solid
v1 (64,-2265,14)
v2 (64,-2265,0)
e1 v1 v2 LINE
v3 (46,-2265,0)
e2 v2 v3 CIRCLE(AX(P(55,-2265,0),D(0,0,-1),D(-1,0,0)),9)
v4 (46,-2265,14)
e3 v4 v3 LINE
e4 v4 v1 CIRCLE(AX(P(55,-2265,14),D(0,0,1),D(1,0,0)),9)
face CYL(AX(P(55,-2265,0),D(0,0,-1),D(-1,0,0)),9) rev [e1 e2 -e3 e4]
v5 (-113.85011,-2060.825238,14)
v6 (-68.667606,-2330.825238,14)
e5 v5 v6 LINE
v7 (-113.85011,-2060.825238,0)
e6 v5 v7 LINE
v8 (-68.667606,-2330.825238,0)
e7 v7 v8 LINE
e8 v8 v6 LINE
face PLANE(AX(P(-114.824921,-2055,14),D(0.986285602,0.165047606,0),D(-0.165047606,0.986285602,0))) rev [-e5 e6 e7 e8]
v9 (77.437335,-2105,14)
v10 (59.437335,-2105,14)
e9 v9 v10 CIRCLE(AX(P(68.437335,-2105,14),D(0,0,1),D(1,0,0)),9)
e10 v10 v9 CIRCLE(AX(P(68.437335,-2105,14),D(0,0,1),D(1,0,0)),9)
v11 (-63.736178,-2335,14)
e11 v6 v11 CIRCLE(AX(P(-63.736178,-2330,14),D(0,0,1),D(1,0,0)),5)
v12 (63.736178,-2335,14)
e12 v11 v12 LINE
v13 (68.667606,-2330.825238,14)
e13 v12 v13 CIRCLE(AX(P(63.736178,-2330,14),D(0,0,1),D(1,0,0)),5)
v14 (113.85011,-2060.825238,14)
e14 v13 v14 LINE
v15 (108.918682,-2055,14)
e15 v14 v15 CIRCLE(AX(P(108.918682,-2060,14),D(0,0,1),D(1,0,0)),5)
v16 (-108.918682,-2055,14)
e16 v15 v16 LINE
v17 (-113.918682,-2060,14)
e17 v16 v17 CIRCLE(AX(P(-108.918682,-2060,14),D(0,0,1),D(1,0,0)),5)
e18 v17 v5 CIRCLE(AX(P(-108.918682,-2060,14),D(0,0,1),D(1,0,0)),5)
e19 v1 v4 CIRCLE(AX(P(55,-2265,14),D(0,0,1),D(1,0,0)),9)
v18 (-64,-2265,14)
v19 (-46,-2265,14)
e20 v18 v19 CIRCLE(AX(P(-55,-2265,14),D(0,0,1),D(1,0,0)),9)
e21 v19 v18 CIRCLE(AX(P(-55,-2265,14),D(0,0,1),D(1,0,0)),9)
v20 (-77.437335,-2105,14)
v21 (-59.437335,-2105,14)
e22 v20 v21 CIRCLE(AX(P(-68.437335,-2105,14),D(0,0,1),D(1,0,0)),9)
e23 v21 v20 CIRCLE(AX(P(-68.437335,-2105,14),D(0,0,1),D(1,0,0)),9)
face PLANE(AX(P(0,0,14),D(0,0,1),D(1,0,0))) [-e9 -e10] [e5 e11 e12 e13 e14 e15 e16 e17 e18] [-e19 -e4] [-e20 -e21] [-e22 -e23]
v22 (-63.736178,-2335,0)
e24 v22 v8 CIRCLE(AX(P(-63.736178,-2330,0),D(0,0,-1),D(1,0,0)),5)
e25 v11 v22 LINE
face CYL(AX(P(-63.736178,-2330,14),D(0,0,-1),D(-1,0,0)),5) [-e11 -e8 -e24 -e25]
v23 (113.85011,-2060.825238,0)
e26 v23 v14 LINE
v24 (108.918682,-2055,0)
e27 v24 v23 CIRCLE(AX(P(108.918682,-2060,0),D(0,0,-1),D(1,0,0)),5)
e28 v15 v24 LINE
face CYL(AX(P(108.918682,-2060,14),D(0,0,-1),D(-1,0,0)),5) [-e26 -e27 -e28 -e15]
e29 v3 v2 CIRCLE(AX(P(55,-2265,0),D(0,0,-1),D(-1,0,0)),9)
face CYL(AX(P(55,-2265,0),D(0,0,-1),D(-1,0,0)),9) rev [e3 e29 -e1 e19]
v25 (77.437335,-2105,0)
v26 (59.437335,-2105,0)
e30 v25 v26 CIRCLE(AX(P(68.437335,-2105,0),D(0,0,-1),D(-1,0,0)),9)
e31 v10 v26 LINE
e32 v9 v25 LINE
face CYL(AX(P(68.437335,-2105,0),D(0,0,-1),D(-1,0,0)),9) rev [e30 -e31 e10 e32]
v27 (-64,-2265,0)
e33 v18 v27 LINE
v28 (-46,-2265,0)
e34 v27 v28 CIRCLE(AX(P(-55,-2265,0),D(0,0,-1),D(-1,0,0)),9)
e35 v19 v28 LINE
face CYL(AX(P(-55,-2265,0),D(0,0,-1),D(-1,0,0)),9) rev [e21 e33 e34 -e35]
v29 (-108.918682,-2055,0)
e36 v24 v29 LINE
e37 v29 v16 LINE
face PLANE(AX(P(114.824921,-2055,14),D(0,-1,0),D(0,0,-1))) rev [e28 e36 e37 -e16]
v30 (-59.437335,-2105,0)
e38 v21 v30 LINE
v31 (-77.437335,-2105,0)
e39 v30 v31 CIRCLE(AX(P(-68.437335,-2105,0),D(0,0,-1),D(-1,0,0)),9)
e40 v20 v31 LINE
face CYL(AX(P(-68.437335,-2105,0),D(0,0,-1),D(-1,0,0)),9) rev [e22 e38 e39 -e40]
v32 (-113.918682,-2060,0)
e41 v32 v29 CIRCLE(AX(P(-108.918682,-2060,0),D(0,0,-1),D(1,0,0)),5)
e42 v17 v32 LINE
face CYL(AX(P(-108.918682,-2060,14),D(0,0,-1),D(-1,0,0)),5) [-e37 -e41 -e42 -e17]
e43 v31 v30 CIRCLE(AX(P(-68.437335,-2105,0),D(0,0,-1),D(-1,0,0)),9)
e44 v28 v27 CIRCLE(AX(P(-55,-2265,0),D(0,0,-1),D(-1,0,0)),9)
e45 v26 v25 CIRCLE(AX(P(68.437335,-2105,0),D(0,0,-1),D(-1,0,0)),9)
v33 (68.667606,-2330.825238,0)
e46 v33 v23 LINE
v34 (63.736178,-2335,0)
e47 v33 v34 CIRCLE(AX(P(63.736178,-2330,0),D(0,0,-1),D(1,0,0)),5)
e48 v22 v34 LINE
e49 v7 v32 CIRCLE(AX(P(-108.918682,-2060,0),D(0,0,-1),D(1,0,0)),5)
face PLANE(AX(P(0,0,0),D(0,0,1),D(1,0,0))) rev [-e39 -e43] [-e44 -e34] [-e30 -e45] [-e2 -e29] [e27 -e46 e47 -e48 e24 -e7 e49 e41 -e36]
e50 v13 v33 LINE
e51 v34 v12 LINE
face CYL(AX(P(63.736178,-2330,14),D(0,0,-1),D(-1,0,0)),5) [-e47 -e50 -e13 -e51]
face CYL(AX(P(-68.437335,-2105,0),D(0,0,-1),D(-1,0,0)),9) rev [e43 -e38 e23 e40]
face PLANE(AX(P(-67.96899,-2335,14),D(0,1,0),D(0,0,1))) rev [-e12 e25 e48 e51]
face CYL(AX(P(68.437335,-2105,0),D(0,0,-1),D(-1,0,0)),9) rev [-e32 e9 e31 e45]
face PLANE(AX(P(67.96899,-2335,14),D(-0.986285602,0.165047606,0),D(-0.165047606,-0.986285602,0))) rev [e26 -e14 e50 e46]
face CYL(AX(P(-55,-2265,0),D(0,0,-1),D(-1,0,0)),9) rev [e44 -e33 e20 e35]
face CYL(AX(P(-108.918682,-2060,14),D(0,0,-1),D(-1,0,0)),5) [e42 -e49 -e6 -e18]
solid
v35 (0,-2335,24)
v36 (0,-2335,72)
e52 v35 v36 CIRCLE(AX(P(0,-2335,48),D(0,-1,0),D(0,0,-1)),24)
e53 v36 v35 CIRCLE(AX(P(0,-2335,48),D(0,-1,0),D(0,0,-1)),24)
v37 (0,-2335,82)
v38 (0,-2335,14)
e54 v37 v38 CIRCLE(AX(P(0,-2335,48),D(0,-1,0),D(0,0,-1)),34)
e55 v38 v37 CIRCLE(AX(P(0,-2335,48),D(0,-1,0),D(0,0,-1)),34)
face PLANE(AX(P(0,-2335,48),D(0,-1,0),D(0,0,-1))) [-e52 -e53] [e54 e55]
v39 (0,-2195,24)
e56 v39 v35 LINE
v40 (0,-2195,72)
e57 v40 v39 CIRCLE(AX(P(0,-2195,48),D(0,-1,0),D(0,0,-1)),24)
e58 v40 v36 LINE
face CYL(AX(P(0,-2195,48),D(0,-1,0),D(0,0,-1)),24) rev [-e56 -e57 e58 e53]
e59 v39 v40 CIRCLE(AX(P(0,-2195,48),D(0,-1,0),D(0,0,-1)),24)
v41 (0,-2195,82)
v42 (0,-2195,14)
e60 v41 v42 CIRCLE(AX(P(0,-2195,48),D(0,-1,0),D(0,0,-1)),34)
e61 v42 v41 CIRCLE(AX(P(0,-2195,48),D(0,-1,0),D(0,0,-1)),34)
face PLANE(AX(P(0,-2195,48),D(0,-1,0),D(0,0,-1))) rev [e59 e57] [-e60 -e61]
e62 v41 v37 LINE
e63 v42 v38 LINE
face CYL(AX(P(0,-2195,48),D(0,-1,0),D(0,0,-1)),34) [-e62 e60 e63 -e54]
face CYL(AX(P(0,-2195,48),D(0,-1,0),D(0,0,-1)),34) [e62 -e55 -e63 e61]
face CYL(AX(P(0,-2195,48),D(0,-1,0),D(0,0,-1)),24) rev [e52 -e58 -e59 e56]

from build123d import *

# Parameters (mm, degrees)
EXTRUDE_1_DEPTH                  = 14
SKETCH_2_R                       = 34
SKETCH_2_R_2                     = 24
EXTRUDE_2_DEPTH                  = 140
FILLET_1_R                       = 5
HOLE_WIZARD_18_0_18_1_AT_2_COUNT = 2
HOLE_WIZARD_18_0_18_1_AT_2_PITCH = 160.563264727
HOLE_WIZARD_18_0_18_1_AT_3_COUNT = 2
HOLE_WIZARD_18_0_18_1_AT_3_PITCH = 202.081111798
HOLE_WIZARD_18_0_18_1_AT_4_COUNT = 2
HOLE_WIZARD_18_0_18_1_AT_4_PITCH = 136.874670595


with BuildPart() as part:
    # 草图1 → 凸台-拉伸1 (new body)
    with BuildSketch(Plane.XY):
        Polygon((-67.968990431, -2335), (67.968990431, -2335), (114.824920973, -2055), (-114.824920973, -2055), align=None)
    extrude(amount=EXTRUDE_1_DEPTH)

    # 圆角1
    fillet_1_edges = [part.edges().sort_by_distance(p)[0] for p in [
        (-114.824920973, -2055, 7),
        (114.824920973, -2055, 7),
        (67.968990431, -2335, 7),
        (-67.968990431, -2335, 7),
    ]]
    fillet(fillet_1_edges, radius=FILLET_1_R)

    # 草图5 → Ø18.0 (18) 直径孔1 (revolve, cut)
    with BuildSketch(Plane(origin=(68.437335298, -2105, 0), x_dir=(0, 1, 0), z_dir=(1, 0, 0))):
        Polygon((0, 0), (0, 65.407745571), (9, 60), (9, 0), align=None)
    hole_wizard_18_0_18_1 = revolve(axis=Axis((68.437335298, -2105, -6.35), (0, 0, 1)), mode=Mode.SUBTRACT)

    # Ø18.0 (18) 直径孔1 at 2: Ø18.0 (18) 直径孔1 ×2
    with Locations(*[Vector(-0.08368872743367663, -0.9964919452261176, 0) * (i * HOLE_WIZARD_18_0_18_1_AT_2_PITCH) for i in range(1, HOLE_WIZARD_18_0_18_1_AT_2_COUNT)]):
        add(hole_wizard_18_0_18_1, mode=Mode.SUBTRACT)

    # Ø18.0 (18) 直径孔1 at 3: Ø18.0 (18) 直径孔1 ×2
    with Locations(*[Vector(-0.6108306422087694, -0.7917612812829524, 0) * (i * HOLE_WIZARD_18_0_18_1_AT_3_PITCH) for i in range(1, HOLE_WIZARD_18_0_18_1_AT_3_COUNT)]):
        add(hole_wizard_18_0_18_1, mode=Mode.SUBTRACT)

    # Ø18.0 (18) 直径孔1 at 4: Ø18.0 (18) 直径孔1 ×2
    with Locations(*[(-i * HOLE_WIZARD_18_0_18_1_AT_4_PITCH, 0, 0) for i in range(1, HOLE_WIZARD_18_0_18_1_AT_4_COUNT)]):
        add(hole_wizard_18_0_18_1, mode=Mode.SUBTRACT)


with BuildPart() as body_2:
    # 草图2 → 凸台-拉伸2 (new body)
    with BuildSketch(Plane.XZ.offset(2335)):
        with Locations(Location((0, 48, 0), (0, 0, 270))):
            Circle(SKETCH_2_R)
        with Locations(Location((0, 48, 0), (0, 0, 270))):
            Circle(SKETCH_2_R_2, mode=Mode.SUBTRACT)
    extrude(amount=-EXTRUDE_2_DEPTH)


solid = Compound([part.part, body_2.part])
